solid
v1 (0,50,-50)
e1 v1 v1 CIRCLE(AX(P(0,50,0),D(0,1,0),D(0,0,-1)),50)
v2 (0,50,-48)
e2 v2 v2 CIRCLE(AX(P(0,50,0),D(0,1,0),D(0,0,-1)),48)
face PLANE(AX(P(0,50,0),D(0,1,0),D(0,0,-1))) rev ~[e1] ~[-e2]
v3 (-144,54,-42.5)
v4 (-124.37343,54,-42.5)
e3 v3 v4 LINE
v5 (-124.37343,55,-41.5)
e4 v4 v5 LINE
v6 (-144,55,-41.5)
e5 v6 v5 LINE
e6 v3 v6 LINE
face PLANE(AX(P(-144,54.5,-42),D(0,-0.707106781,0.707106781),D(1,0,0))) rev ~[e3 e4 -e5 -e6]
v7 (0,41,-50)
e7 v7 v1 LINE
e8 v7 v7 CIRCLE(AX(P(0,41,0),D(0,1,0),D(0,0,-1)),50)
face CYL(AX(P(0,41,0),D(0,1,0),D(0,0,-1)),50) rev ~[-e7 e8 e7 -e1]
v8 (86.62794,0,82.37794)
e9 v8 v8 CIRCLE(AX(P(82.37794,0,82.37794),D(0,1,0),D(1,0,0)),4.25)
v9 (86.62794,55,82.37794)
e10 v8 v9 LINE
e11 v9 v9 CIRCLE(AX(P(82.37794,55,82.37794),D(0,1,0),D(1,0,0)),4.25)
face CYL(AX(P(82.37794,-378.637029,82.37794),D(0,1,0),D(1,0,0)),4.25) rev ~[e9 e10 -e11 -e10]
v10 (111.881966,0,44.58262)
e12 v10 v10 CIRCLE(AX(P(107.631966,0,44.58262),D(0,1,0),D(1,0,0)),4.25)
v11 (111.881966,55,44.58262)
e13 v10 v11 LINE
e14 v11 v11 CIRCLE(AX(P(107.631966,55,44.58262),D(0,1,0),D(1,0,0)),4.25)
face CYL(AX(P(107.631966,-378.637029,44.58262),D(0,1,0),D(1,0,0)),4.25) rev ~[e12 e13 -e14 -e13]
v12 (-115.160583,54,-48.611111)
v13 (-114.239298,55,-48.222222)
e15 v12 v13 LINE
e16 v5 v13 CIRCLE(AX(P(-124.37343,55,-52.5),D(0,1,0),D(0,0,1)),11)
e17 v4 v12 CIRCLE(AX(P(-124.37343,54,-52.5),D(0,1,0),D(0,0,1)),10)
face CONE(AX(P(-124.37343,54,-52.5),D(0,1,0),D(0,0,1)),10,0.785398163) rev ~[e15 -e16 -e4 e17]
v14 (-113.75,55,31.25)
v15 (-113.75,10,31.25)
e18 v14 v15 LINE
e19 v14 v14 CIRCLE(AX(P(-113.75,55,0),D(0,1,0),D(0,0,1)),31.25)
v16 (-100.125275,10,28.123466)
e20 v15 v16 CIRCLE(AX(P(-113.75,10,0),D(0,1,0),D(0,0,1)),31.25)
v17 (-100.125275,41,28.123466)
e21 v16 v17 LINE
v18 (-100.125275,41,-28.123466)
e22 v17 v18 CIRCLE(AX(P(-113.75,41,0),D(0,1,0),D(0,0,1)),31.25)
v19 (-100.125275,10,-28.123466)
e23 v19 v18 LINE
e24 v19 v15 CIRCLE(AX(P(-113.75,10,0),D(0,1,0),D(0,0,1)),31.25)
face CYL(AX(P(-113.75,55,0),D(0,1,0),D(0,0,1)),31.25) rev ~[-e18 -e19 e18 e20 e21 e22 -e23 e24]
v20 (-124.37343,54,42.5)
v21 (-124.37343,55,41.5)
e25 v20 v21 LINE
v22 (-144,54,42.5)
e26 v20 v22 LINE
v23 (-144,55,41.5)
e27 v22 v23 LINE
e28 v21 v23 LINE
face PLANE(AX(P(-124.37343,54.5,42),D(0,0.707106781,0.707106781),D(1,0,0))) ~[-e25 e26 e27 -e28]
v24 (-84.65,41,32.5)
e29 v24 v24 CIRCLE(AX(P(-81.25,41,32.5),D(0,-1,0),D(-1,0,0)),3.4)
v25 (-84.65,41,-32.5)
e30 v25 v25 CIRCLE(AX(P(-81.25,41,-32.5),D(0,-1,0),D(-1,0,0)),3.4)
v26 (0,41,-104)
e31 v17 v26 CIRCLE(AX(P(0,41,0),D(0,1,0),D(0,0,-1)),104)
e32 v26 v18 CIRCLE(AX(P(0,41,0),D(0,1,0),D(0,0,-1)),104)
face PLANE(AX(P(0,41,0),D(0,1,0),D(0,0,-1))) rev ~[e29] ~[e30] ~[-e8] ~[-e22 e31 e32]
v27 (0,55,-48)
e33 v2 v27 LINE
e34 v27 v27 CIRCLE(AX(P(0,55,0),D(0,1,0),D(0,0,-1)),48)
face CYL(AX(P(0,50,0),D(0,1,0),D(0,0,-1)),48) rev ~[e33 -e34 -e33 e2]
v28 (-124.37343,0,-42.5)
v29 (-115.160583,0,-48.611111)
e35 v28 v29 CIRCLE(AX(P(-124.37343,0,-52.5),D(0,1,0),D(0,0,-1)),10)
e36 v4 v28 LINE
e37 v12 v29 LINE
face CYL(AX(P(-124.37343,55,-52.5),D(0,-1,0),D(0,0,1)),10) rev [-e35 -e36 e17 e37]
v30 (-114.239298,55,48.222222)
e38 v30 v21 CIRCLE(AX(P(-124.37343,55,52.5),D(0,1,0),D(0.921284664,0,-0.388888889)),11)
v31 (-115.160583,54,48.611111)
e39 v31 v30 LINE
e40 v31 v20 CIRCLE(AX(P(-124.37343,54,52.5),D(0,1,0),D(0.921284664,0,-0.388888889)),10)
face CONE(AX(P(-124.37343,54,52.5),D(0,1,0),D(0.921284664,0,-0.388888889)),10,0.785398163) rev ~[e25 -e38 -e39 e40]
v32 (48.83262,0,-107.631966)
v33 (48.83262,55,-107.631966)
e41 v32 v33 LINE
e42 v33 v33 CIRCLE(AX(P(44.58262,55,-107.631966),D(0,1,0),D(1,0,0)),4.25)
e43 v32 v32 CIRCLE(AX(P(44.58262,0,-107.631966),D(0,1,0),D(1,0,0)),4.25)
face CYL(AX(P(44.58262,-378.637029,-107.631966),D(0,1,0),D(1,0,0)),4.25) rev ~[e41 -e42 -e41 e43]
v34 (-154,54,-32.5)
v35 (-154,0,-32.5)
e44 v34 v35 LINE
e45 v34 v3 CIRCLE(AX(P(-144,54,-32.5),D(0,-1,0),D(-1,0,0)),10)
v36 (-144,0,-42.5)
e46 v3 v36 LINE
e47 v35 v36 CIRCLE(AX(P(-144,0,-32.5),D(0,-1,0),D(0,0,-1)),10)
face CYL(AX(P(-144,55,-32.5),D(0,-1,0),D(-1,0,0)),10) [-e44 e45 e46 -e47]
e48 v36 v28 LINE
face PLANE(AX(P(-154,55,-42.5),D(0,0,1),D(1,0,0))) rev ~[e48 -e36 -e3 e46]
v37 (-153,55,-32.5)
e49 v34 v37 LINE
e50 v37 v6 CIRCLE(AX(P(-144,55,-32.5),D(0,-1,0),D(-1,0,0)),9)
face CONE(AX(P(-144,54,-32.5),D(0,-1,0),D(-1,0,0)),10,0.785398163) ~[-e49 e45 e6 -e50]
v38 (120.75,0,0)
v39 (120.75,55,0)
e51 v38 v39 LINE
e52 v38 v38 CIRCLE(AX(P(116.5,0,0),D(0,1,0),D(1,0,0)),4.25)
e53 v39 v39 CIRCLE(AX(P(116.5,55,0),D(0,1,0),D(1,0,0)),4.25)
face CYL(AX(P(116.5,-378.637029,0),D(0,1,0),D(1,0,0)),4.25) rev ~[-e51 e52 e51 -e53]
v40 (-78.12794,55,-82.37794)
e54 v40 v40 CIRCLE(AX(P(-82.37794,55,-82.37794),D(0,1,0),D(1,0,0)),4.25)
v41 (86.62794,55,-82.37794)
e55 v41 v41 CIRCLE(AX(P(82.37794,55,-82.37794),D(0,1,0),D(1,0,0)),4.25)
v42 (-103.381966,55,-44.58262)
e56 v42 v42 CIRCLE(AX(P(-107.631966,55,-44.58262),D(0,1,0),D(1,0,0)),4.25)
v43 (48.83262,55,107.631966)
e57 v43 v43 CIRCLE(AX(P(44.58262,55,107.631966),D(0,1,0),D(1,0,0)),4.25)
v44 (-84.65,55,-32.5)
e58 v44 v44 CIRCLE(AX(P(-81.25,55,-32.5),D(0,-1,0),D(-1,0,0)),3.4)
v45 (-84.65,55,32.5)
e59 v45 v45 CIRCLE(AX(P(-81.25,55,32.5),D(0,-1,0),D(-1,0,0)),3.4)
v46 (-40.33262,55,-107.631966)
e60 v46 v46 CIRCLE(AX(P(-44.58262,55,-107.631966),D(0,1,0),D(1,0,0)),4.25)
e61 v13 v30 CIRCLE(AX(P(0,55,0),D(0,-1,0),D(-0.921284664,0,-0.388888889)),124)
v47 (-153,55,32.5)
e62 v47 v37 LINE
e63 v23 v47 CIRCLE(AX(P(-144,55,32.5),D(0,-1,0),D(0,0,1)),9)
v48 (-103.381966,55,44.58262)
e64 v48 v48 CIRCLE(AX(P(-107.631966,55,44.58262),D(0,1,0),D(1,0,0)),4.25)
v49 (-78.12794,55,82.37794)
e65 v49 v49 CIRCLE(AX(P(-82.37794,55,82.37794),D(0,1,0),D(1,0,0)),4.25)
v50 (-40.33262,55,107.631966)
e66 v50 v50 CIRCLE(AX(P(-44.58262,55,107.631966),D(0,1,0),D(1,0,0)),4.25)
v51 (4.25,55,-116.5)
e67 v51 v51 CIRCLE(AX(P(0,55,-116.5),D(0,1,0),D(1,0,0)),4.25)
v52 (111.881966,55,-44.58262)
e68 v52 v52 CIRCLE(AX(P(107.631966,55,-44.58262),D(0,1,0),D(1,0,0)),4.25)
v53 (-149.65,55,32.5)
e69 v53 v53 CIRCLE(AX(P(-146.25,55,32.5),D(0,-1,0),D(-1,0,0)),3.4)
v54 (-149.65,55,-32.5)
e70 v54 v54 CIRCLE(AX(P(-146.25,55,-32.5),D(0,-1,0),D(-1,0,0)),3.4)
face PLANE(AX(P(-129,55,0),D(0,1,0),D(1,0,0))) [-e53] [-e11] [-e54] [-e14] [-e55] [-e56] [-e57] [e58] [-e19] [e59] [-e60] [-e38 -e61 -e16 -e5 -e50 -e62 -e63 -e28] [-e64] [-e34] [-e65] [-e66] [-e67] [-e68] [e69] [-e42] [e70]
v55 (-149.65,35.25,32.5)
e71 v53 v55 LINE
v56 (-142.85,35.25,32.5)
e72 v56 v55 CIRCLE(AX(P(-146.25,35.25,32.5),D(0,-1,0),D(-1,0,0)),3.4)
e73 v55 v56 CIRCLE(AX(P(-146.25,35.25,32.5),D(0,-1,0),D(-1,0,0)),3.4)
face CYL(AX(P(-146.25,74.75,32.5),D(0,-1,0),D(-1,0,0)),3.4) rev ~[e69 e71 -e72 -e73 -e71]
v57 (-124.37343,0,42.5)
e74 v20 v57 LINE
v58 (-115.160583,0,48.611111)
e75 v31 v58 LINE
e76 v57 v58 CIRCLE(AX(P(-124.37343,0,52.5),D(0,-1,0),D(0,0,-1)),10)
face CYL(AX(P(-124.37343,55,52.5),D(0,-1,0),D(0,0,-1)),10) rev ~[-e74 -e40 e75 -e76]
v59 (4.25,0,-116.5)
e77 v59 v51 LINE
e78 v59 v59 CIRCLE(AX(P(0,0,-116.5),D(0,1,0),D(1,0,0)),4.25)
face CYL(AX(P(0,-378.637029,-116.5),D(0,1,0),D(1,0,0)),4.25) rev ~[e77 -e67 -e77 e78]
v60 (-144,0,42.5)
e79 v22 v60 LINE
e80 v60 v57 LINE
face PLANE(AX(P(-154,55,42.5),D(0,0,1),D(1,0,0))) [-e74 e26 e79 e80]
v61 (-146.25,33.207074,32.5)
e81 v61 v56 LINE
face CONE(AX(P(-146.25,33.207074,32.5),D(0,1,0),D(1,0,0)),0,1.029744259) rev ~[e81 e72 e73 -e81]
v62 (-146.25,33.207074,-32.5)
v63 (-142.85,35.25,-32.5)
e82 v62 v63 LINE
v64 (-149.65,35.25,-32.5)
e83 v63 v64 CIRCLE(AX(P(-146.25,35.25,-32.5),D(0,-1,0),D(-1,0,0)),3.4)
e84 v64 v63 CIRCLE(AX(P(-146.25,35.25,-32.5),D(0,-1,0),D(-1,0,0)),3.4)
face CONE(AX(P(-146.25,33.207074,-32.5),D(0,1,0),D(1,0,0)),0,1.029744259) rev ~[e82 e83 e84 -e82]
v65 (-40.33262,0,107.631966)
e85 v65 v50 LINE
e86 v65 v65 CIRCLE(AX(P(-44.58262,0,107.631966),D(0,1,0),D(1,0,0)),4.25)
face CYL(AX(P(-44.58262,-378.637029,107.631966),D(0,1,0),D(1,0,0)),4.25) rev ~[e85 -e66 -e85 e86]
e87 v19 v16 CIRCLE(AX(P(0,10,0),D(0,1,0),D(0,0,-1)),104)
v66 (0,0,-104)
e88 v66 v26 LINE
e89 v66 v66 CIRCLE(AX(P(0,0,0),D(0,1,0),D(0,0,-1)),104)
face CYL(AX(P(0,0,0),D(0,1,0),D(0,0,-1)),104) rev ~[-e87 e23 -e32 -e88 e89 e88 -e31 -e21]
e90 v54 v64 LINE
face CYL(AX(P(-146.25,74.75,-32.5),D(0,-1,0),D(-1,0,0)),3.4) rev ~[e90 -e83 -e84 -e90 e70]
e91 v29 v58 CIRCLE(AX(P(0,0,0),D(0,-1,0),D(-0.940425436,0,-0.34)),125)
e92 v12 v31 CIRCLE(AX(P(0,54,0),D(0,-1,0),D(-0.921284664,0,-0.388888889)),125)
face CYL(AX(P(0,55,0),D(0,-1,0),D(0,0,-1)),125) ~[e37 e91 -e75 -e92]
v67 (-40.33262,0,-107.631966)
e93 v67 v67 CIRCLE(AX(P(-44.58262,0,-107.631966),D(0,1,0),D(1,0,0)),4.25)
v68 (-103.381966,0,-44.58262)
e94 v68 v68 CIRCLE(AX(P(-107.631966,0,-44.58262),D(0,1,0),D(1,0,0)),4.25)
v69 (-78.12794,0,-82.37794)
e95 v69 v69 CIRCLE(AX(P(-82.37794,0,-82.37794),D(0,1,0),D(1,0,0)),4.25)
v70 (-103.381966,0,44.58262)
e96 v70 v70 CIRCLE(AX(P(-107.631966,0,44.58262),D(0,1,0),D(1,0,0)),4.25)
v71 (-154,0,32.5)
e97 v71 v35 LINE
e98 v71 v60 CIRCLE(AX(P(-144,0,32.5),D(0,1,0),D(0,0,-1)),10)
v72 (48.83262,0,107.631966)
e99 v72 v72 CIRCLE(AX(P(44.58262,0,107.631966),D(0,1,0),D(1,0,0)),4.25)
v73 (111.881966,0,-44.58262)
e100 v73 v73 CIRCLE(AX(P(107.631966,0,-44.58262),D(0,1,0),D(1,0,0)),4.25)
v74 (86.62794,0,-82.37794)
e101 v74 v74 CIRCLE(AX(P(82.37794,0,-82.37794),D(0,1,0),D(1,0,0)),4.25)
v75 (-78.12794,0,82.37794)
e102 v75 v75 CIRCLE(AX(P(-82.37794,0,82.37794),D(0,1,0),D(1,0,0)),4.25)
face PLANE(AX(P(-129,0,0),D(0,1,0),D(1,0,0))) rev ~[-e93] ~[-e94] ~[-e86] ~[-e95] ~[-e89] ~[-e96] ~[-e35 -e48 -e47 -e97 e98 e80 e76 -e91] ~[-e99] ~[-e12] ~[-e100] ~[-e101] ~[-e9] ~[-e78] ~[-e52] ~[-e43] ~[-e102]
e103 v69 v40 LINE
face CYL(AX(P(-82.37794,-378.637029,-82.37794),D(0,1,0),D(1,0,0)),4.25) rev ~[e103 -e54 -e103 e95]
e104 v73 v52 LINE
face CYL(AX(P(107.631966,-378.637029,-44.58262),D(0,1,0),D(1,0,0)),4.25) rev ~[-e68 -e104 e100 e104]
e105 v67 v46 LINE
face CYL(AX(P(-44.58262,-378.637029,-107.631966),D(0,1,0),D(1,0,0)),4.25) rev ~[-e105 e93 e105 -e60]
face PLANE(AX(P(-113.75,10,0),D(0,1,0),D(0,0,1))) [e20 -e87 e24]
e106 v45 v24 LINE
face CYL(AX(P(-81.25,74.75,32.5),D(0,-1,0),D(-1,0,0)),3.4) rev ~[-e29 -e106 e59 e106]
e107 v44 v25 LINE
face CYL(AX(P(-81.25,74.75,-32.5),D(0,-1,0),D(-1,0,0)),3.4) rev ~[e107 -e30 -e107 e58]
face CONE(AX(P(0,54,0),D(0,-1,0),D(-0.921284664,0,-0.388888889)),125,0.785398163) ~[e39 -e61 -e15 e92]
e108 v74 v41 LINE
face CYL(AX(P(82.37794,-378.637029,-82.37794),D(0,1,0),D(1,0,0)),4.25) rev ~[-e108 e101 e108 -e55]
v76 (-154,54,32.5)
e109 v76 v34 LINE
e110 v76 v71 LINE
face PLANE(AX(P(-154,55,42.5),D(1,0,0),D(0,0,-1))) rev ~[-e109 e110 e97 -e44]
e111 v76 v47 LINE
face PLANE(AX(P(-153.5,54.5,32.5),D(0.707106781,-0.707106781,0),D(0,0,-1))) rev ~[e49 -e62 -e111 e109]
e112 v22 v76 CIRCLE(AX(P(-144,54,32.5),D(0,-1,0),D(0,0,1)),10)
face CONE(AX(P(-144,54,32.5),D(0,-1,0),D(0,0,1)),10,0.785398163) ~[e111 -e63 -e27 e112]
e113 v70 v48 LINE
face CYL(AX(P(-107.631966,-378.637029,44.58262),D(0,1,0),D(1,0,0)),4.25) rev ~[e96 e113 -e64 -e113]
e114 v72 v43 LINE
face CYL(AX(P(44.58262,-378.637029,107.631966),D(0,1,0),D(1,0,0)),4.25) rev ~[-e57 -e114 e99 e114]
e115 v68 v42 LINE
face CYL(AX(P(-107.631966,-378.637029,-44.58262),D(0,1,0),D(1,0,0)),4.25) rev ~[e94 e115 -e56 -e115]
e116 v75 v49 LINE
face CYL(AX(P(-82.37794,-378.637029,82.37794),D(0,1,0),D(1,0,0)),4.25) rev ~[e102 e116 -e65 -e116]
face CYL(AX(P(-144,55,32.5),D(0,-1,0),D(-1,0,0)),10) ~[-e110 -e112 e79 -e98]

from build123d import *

# Parameters (mm, degrees)
SKETCH_3_W             = 50
SKETCH_3_H             = 85
EXTRUDE_1_DEPTH        = 55
SKETCH_5_R             = 31.25
CUT_EXTRUDE_1_DEPTH    = 45
HOLE_WIZARD_M8_1_D     = 6.8
HOLE_WIZARD_M8_1_DEPTH = 19.75
HOLE_WIZARD_M8_1_TIP   = 2.042926105
FILLET_1_R             = 10
HOLE_WIZARD_M10_1_D    = 8.5
CHAMFER_1_SIZE         = 1


with BuildPart() as part:
    # 草图2 → 旋转1 (revolve)
    with BuildSketch(Plane.XY, mode=Mode.PRIVATE) as revolve_1_sk:
        Polygon((104, 0), (104, 41), (50, 41), (50, 50), (48, 50), (48, 55), (125, 55), (125, 0), align=None)
    revolve(revolve_1_sk.sketch.rotate(Axis((0, 0, 0), (0, 1, 0)), 90), axis=Axis((0, 0, 0), (0, 1, 0)))

    # 草图3 → 凸台-拉伸1 (add, through all)
    with BuildSketch(Plane(origin=(0, 55, 0), x_dir=(1, 0, 0), z_dir=(0, 1, 0))):
        with Locations((-129, 0)):
            Rectangle(SKETCH_3_W, SKETCH_3_H)
    extrude(amount=-EXTRUDE_1_DEPTH)

    # 草图5 → 切除-拉伸1 (cut)
    with BuildSketch(Plane(origin=(0, 55, 0), x_dir=(1, 0, 0), z_dir=(0, 1, 0))):
        with Locations(Location((-113.75, 0, 0), (0, 0, 270))):
            Circle(SKETCH_5_R)
    extrude(amount=-CUT_EXTRUDE_1_DEPTH, mode=Mode.SUBTRACT)

    # M8 螺纹孔1
    with Locations(Plane(origin=(0, 55, 0), x_dir=(1, 0, 0), z_dir=(0, 1, 0))):
        with Locations((-146.25, 32.5), (-113.75, 0), (-81.25, 32.5), (-146.25, -32.5), (-81.25, -32.5)):
            Hole(HOLE_WIZARD_M8_1_D / 2, depth=HOLE_WIZARD_M8_1_DEPTH)
            with Locations((0, 0, -(HOLE_WIZARD_M8_1_DEPTH + HOLE_WIZARD_M8_1_TIP / 2))):  # 118° drill point
                Cone(0, HOLE_WIZARD_M8_1_D / 2, HOLE_WIZARD_M8_1_TIP, mode=Mode.SUBTRACT)

    # 圆角1
    fillet_1_edges = [part.edges().sort_by_distance(p)[0] for p in [
        (-117.553179455, 27.5, 42.5),
        (-117.553179455, 27.5, -42.5),
        (-154, 27.5, 42.5),
        (-154, 27.5, -42.5),
    ]]
    fillet(fillet_1_edges, radius=FILLET_1_R)

    # M10 螺纹孔1 (through all)
    with Locations(Plane(origin=(0, 0, 0), x_dir=(-1, 0, 0), z_dir=(0, -1, 0))):
        with Locations((-107.631965538, -44.582619871), (-107.631965538, 44.582619871), (-44.582619871, 107.631965538), (44.582619871, 107.631965538), (107.631965538, 44.582619871), (107.631965538, -44.582619871), (44.582619871, -107.631965538), (-44.582619871, -107.631965538), (0, 116.5), (-82.377940008, 82.377940008), (82.377940008, 82.377940008), (-82.377940008, -82.377940008), (82.377940008, -82.377940008), (-116.5, 0)):
            Hole(HOLE_WIZARD_M10_1_D / 2)

    # 倒角1
    chamfer_1_edges = [part.edges().sort_by_distance(p)[0] for p in [
        (-154, 55, 0),
        (125, 55, 0),
        (-134.186714819, 55, -42.5),
        (-134.186714819, 55, 42.5),
        (-151.071067812, 55, -39.571067812),
        (-151.071067812, 55, 39.571067812),
        (-118.845721654, 55, -44.166666667),
        (-118.845721654, 55, 44.166666667),
    ]]
    chamfer(chamfer_1_edges, length=CHAMFER_1_SIZE)


solid = part.part
